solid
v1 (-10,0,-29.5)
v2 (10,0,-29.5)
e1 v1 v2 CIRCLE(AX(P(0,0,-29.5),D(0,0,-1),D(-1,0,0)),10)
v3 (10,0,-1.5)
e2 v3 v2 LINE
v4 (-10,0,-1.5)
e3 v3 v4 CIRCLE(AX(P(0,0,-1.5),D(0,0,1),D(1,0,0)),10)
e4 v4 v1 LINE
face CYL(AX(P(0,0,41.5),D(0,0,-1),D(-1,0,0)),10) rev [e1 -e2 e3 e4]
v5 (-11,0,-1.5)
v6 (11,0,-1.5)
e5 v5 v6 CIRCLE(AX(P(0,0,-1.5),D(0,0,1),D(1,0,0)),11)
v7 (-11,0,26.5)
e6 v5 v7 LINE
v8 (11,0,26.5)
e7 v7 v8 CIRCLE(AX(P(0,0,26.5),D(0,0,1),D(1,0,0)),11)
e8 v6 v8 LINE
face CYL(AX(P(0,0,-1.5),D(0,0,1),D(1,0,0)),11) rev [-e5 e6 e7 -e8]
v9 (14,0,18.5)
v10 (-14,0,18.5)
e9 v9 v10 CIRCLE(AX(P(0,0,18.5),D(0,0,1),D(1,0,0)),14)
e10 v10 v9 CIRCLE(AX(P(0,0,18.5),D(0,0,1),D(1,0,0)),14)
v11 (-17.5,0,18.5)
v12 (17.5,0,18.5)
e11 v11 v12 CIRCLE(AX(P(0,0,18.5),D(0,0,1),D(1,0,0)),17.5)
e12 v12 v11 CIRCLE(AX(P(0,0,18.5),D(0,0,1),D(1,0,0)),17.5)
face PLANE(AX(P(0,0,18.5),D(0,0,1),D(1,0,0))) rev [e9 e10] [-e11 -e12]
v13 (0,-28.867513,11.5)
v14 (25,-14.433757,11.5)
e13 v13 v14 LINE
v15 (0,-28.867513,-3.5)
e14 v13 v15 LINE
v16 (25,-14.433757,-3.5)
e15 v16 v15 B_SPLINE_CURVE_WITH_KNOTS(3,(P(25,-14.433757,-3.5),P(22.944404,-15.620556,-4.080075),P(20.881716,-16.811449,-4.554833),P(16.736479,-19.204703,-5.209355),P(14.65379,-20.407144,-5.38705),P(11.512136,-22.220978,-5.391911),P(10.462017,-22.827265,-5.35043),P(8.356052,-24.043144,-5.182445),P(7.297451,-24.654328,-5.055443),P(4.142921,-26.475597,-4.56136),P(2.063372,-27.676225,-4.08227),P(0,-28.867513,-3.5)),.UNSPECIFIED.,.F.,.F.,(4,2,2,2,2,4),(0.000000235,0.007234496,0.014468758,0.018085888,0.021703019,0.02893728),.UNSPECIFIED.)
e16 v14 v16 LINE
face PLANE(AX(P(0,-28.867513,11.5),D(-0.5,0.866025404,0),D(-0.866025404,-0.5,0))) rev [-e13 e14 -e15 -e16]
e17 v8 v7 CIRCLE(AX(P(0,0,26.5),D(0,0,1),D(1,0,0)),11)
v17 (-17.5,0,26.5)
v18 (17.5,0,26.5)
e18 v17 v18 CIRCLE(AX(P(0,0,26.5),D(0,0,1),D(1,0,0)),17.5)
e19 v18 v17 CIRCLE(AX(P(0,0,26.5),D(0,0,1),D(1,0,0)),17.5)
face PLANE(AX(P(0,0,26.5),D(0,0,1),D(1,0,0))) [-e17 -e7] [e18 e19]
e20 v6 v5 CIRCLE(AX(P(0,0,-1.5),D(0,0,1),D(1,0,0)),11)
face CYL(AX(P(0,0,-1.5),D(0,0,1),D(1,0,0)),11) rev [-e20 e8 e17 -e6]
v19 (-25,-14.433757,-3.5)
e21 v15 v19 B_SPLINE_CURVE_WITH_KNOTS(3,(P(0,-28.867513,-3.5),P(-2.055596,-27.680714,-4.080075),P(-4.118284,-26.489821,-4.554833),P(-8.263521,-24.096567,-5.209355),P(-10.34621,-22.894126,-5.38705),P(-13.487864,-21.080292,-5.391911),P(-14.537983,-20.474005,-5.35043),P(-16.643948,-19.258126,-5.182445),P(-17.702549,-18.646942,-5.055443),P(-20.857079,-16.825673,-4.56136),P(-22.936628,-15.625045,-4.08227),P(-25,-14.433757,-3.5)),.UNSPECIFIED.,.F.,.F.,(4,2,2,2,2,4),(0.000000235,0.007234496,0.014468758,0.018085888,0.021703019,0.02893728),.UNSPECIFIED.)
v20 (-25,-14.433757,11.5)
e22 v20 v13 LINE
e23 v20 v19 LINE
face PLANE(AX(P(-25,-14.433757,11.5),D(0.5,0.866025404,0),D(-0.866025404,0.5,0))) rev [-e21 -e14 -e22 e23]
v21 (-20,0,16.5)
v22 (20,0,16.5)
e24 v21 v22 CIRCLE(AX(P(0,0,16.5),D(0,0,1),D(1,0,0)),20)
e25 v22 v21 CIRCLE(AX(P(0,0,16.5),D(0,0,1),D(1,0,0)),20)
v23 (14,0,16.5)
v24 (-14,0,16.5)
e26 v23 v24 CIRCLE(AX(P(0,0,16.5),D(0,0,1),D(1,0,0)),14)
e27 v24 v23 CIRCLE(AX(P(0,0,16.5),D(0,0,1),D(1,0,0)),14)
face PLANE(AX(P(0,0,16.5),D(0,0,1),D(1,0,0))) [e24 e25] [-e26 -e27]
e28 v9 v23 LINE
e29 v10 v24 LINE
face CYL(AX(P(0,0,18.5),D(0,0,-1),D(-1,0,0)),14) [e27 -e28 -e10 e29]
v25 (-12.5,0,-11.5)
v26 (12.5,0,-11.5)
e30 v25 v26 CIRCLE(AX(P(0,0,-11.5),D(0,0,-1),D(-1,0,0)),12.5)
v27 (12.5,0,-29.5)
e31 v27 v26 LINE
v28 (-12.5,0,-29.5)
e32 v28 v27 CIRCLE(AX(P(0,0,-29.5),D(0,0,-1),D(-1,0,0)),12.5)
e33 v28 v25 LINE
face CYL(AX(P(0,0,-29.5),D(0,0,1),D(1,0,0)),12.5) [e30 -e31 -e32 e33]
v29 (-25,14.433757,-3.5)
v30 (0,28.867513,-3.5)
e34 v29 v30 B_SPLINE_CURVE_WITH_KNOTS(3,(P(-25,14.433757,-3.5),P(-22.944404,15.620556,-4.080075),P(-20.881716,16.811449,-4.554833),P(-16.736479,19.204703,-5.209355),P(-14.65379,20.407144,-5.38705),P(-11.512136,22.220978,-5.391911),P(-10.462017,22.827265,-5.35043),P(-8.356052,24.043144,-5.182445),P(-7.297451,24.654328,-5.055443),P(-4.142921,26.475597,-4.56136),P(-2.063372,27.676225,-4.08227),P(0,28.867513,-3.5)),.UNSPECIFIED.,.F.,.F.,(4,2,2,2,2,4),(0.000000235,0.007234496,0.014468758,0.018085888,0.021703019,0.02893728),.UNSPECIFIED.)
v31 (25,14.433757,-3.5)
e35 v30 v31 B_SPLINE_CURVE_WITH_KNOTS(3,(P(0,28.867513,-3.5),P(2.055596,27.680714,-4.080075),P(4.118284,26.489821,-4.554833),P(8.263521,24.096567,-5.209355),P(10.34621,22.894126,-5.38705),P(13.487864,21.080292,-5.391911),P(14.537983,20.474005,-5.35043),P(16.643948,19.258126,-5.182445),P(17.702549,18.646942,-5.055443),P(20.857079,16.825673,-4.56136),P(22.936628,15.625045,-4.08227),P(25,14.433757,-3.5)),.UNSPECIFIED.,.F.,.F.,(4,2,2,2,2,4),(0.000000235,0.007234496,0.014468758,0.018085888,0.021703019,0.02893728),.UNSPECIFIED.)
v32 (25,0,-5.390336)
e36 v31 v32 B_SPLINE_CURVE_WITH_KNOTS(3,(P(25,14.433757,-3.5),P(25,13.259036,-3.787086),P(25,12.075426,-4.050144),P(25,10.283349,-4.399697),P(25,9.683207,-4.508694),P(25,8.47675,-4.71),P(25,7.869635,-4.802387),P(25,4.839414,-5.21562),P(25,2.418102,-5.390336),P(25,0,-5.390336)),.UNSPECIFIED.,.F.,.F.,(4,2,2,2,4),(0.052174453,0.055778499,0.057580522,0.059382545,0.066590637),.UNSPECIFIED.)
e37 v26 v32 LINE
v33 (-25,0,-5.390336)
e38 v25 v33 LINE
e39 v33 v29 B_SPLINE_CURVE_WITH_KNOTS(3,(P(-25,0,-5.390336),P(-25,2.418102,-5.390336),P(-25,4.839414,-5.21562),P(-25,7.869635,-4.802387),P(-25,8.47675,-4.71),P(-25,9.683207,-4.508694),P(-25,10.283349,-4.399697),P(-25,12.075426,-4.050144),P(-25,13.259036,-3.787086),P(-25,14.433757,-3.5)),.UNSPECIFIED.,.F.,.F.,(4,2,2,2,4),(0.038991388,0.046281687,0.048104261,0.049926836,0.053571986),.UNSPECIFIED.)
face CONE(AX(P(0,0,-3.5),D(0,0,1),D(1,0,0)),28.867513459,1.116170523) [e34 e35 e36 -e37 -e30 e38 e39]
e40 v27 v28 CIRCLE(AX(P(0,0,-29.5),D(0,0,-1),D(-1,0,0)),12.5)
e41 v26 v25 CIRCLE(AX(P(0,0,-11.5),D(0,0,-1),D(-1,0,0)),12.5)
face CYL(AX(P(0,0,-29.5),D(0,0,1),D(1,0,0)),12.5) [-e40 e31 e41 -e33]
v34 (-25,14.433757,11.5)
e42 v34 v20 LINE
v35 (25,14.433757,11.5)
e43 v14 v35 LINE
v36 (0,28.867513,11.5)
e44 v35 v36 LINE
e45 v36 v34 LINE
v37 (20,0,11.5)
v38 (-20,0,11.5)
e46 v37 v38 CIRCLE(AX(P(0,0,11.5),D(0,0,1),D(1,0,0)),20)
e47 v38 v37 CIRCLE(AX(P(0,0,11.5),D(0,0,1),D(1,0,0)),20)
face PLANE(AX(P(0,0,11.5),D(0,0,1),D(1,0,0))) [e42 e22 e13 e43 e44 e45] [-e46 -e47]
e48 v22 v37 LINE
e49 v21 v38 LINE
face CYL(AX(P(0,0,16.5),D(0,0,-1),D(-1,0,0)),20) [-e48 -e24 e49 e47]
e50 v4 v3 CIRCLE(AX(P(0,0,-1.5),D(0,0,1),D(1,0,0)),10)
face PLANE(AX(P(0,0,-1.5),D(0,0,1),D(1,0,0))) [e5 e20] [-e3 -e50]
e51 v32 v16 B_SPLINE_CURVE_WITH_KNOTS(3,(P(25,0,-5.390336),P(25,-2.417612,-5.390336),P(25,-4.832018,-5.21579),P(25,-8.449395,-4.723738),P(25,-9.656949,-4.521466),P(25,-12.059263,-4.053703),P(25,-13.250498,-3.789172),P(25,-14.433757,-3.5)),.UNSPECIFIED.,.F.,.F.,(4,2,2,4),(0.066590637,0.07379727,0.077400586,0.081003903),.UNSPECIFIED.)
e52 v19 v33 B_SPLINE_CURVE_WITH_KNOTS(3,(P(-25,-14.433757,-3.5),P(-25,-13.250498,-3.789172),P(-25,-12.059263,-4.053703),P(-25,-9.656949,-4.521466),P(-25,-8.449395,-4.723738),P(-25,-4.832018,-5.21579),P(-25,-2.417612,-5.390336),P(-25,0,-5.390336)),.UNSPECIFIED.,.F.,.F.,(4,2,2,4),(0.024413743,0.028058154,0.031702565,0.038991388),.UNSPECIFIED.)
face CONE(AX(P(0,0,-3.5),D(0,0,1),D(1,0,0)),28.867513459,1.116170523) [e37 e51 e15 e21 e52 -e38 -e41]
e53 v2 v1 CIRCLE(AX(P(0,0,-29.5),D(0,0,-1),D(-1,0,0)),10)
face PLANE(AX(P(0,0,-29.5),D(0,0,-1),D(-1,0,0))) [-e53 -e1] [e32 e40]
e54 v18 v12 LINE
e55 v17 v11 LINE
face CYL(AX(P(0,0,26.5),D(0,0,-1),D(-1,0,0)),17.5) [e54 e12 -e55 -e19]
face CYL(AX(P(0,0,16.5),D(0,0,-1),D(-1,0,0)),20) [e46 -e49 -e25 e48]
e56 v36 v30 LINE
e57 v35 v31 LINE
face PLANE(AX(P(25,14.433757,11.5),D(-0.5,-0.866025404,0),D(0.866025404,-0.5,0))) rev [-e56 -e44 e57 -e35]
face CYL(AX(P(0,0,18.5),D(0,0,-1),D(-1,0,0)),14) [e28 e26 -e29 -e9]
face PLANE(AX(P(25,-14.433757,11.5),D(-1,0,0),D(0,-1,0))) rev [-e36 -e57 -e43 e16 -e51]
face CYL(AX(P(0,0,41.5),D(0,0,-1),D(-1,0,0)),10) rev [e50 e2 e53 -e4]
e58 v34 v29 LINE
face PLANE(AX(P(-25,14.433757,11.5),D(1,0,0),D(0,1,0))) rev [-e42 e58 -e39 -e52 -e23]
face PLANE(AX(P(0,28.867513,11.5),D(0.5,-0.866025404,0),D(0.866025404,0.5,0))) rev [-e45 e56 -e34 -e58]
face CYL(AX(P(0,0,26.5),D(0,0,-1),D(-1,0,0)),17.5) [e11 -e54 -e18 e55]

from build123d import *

# Parameters (mm, degrees)
BOSS_EXTRUDE1_DEPTH = 11.5
SKETCH4_R           = 12.5
BOSS_EXTRUDE2_DEPTH = 18
SKETCH5_R           = 20
BOSS_EXTRUDE3_DEPTH = 5
SKETCH6_R           = 14
BOSS_EXTRUDE4_DEPTH = 2
SKETCH7_R           = 17.5
BOSS_EXTRUDE5_DEPTH = 8
SKETCH8_R           = 11
CUT_EXTRUDE1_DEPTH  = 28
SKETCH9_R           = 10
CUT_EXTRUDE2_DEPTH  = 71


with BuildPart() as part:
    # Sketch1 → Boss-Extrude1 (new, symmetric)
    with BuildSketch(Plane.XY):
        Polygon((0, 28.867513459), (-25, 14.43375673), (-25, -14.43375673), (0, -28.867513459), (25, -14.43375673), (25, 14.43375673), align=None)
    extrude(amount=BOSS_EXTRUDE1_DEPTH, both=True)

    # Sketch3 → Cut-Revolve1 (revolve, cut)
    with BuildSketch(Plane(origin=(0, 0, 0), x_dir=(0, 0, -1), z_dir=(1, 0, 0)), mode=Mode.PRIVATE) as cut_revolve1_sk:
        Polygon((11.5, 12.5), (3.5, 28.867513459), (11.5, 28.867513459), align=None)
    revolve(cut_revolve1_sk.sketch.rotate(Axis((0, 0, 1000), (0, 0, -1)), 90), axis=Axis((0, 0, 1000), (0, 0, -1)), mode=Mode.SUBTRACT)

    # Sketch4 → Boss-Extrude2 (add)
    with BuildSketch(Plane(origin=(0, 0, -11.5), x_dir=(-1, 0, 0), z_dir=(0, 0, -1))):
        Circle(SKETCH4_R)
    extrude(amount=BOSS_EXTRUDE2_DEPTH)

    # Sketch5 → Boss-Extrude3 (add)
    with BuildSketch(Plane.XY.offset(11.5)):
        Circle(SKETCH5_R)
    extrude(amount=BOSS_EXTRUDE3_DEPTH)

    # Sketch6 → Boss-Extrude4 (add)
    with BuildSketch(Plane.XY.offset(16.5)):
        Circle(SKETCH6_R)
    extrude(amount=BOSS_EXTRUDE4_DEPTH)

    # Sketch7 → Boss-Extrude5 (add)
    with BuildSketch(Plane.XY.offset(18.5)):
        Circle(SKETCH7_R)
    extrude(amount=BOSS_EXTRUDE5_DEPTH)

    # Sketch8 → Cut-Extrude1 (cut)
    with BuildSketch(Plane.XY.offset(26.5)):
        Circle(SKETCH8_R)
    extrude(amount=-CUT_EXTRUDE1_DEPTH, mode=Mode.SUBTRACT)

    # Sketch9 → Cut-Extrude2 (cut)
    with BuildSketch(Plane(origin=(0, 0, -29.5), x_dir=(-1, 0, 0), z_dir=(0, 0, -1))):
        Circle(SKETCH9_R)
    extrude(amount=-CUT_EXTRUDE2_DEPTH, mode=Mode.SUBTRACT)


solid = part.part
